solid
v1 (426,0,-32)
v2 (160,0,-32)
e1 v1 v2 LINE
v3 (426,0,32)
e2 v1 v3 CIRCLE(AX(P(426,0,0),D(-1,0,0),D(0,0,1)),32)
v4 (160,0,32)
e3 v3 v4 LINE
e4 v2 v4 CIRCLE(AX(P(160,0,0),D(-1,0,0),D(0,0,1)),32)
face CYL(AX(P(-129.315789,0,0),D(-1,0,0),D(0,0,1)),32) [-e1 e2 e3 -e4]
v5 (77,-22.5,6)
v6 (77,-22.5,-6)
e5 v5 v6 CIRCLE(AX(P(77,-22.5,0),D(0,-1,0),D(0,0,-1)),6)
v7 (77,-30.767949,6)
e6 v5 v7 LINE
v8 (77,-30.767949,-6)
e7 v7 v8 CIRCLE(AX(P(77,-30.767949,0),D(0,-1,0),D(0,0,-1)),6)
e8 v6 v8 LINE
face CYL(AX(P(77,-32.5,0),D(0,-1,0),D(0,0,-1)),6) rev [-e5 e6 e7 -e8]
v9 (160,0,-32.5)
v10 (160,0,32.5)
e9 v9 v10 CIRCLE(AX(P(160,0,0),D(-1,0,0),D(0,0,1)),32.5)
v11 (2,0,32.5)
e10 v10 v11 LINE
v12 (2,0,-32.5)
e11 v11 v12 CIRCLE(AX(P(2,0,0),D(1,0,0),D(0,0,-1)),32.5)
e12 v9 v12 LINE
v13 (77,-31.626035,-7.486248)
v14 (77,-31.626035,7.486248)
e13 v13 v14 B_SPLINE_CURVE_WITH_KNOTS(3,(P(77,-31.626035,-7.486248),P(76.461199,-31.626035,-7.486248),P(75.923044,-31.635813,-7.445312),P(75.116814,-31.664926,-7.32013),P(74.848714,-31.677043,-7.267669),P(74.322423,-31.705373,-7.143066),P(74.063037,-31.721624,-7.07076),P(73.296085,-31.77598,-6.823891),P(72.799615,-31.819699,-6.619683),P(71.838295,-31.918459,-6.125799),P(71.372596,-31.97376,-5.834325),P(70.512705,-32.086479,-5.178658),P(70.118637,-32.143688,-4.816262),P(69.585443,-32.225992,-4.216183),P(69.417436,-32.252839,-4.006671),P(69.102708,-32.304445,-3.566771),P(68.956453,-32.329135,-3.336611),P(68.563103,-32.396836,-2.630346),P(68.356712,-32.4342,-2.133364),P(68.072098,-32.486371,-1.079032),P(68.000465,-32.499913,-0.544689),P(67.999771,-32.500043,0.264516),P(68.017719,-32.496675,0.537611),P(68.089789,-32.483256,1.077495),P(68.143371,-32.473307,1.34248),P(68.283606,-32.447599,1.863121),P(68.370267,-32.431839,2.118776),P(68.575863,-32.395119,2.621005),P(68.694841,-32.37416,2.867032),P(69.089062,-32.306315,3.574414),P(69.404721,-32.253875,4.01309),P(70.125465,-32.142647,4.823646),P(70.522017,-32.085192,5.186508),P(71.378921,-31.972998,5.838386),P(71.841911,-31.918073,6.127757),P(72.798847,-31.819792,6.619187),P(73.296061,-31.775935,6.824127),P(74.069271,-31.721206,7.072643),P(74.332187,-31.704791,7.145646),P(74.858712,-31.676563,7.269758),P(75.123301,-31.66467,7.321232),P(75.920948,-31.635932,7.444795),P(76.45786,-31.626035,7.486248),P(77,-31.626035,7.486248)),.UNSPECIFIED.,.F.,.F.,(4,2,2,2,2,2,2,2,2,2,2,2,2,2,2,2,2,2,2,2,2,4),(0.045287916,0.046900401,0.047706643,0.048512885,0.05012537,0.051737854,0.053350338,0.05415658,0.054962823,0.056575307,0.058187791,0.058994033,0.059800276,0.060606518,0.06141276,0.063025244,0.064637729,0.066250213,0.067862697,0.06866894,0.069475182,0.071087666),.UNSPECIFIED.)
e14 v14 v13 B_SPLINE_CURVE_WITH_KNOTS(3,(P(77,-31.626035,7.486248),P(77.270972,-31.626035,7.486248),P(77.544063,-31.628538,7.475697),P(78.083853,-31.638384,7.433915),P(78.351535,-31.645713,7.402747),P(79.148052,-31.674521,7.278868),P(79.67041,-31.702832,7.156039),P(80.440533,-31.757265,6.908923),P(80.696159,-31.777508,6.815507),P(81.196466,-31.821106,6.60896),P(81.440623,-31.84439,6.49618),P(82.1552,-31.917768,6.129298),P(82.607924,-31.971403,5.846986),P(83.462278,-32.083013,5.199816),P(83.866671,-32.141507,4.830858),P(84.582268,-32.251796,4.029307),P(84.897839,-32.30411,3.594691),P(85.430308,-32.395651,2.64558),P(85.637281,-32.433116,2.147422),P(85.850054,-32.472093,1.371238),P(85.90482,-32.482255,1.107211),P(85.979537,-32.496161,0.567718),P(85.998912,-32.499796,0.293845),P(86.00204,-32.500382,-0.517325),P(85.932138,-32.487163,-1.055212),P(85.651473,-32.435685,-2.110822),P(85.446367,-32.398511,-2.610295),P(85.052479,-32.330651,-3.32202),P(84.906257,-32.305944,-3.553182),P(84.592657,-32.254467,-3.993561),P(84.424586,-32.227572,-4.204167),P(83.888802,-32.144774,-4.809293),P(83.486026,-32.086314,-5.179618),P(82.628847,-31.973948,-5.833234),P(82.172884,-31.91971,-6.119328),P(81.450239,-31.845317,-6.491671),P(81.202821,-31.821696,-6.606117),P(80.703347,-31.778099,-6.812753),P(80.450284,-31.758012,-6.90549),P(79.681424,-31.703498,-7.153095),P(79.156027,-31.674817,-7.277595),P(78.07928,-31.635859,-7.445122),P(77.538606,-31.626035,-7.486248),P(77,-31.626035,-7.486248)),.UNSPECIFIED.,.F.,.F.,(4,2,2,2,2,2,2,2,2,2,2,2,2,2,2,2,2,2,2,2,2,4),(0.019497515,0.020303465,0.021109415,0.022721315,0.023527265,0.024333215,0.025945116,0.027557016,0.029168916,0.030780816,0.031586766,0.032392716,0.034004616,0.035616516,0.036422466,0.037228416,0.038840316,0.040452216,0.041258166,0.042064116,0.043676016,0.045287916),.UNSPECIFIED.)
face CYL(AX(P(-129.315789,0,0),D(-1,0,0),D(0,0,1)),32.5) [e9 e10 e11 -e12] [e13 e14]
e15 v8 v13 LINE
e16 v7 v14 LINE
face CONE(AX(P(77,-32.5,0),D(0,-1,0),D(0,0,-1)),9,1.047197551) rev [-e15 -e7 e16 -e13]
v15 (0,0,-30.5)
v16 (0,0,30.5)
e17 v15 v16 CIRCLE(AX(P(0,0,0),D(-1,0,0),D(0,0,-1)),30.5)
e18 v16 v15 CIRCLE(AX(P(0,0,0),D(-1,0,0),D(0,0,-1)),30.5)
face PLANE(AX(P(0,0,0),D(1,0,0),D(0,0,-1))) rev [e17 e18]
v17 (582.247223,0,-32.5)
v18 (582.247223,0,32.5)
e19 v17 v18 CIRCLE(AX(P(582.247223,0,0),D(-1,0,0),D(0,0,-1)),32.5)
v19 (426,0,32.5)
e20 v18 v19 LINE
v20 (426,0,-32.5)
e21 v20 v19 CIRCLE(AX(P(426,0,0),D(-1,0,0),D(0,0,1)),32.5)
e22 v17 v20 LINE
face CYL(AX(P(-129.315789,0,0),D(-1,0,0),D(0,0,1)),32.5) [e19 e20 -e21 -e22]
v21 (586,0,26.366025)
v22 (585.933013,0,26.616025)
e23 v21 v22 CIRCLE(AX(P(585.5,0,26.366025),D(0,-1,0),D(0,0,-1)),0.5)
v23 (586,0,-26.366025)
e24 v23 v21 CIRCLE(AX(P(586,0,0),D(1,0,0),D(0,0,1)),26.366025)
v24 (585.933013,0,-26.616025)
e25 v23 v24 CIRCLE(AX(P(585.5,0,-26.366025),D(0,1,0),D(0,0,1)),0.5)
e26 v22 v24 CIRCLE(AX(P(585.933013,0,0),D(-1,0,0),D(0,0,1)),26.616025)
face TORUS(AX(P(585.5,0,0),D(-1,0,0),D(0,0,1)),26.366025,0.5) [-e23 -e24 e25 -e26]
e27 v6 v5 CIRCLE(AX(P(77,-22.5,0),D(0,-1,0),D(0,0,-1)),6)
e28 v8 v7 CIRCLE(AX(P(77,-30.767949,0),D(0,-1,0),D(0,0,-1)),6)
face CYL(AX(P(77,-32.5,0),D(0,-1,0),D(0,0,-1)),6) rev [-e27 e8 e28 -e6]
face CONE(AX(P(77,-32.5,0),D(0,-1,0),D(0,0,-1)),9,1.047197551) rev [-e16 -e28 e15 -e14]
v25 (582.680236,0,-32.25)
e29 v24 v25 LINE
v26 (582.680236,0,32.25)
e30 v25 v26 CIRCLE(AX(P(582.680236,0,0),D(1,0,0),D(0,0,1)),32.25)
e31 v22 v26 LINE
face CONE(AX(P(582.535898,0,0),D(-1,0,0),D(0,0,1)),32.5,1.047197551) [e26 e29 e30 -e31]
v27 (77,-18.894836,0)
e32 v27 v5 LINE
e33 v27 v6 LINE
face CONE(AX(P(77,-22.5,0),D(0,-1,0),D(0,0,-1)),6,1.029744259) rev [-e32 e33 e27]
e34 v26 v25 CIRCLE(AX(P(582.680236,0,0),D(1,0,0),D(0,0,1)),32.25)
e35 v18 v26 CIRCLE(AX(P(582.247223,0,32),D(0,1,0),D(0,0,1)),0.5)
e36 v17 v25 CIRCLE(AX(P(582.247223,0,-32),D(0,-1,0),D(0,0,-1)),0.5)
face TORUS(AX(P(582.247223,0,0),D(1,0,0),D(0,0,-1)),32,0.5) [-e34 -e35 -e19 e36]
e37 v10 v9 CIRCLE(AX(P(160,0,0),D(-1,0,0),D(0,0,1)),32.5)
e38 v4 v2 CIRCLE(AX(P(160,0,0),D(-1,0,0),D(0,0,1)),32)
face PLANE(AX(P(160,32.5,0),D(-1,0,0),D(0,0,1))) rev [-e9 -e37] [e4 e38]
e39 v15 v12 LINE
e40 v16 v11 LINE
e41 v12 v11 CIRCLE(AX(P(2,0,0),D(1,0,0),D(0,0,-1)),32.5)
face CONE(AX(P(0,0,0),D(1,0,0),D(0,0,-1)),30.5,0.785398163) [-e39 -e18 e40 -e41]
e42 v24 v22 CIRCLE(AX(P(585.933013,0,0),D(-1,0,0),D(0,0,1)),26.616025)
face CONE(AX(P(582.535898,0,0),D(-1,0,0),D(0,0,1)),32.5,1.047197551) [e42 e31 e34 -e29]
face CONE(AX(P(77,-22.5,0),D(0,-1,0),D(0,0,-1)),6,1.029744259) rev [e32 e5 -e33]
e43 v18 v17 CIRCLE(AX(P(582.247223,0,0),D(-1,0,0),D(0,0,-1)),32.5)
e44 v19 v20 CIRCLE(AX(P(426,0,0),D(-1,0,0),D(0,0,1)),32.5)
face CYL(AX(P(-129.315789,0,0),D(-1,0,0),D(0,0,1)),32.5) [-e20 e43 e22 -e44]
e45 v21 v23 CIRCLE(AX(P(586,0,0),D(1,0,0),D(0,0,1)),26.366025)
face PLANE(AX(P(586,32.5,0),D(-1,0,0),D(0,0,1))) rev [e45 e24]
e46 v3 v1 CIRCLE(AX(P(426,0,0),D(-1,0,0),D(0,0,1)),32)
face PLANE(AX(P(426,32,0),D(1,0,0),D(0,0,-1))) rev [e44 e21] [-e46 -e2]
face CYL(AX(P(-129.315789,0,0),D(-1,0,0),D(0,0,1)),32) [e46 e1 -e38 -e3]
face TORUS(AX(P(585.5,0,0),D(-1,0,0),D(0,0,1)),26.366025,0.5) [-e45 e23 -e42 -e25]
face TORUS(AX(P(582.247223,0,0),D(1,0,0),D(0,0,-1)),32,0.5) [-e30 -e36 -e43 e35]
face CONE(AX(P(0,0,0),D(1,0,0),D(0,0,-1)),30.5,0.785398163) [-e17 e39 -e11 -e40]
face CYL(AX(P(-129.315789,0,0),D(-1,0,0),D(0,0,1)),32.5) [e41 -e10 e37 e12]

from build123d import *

# Parameters (mm, degrees)
CHAMFER_1_SIZE   = 2
CHAMFER_2_SIZE   = 6
CHAMFER_2_SIZE2  = 3.464101615
FILLET_1_R       = 0.5
MM_2_D           = 12
MM_2_DEPTH       = 10
MM_2_CSINK_D     = 18
MM_2_CSINK_ANGLE = 120
MM_2_TIP         = 3.605163714


with BuildPart() as part:
    # 草图1 → 旋转1 (revolve)
    with BuildSketch(Plane.XY, mode=Mode.PRIVATE) as revolve_1_sk:
        Polygon((0, 32.5), (160, 32.5), (160, 32), (426, 32), (426, 32.5), (586, 32.5), (586, 0), (0, 0), align=None)
    revolve(revolve_1_sk.sketch.rotate(Axis((-129.315789474, 0, 0), (1, 0, 0)), 90), axis=Axis((-129.315789474, 0, 0), (1, 0, 0)))

    # 倒角1
    chamfer_1_edges = [part.edges().sort_by_distance(p)[0] for p in [
        (0, 0, -32.5),
    ]]
    chamfer(chamfer_1_edges, length=CHAMFER_1_SIZE)

    # 倒角2
    chamfer_2_edges = [part.edges().sort_by_distance(p)[0] for p in [
        (586, 0, -32.5),
    ]]
    chamfer_2_side = [part.faces().sort_by_distance(p)[0] for p in [
        (586, 0, 0),
    ]]
    chamfer(chamfer_2_edges, length=CHAMFER_2_SIZE, length2=CHAMFER_2_SIZE2, reference=chamfer_2_side[0])

    # 圆角1
    fillet_1_edges = [part.edges().sort_by_distance(p)[0] for p in [
        (582.535898385, 0, -32.5),
        (586, 0, -26.5),
    ]]
    fillet(fillet_1_edges, radius=FILLET_1_R)

    # 大小mm 暗销孔2
    with Locations(Plane.XZ.offset(32.5)):
        with Locations((77, 0)):
            CounterSinkHole(MM_2_D / 2, MM_2_CSINK_D / 2, depth=MM_2_DEPTH, counter_sink_angle=MM_2_CSINK_ANGLE)
            with Locations((0, 0, -(MM_2_DEPTH + MM_2_TIP / 2))):  # 118° drill point
                Cone(0, MM_2_D / 2, MM_2_TIP, mode=Mode.SUBTRACT)


solid = part.part
